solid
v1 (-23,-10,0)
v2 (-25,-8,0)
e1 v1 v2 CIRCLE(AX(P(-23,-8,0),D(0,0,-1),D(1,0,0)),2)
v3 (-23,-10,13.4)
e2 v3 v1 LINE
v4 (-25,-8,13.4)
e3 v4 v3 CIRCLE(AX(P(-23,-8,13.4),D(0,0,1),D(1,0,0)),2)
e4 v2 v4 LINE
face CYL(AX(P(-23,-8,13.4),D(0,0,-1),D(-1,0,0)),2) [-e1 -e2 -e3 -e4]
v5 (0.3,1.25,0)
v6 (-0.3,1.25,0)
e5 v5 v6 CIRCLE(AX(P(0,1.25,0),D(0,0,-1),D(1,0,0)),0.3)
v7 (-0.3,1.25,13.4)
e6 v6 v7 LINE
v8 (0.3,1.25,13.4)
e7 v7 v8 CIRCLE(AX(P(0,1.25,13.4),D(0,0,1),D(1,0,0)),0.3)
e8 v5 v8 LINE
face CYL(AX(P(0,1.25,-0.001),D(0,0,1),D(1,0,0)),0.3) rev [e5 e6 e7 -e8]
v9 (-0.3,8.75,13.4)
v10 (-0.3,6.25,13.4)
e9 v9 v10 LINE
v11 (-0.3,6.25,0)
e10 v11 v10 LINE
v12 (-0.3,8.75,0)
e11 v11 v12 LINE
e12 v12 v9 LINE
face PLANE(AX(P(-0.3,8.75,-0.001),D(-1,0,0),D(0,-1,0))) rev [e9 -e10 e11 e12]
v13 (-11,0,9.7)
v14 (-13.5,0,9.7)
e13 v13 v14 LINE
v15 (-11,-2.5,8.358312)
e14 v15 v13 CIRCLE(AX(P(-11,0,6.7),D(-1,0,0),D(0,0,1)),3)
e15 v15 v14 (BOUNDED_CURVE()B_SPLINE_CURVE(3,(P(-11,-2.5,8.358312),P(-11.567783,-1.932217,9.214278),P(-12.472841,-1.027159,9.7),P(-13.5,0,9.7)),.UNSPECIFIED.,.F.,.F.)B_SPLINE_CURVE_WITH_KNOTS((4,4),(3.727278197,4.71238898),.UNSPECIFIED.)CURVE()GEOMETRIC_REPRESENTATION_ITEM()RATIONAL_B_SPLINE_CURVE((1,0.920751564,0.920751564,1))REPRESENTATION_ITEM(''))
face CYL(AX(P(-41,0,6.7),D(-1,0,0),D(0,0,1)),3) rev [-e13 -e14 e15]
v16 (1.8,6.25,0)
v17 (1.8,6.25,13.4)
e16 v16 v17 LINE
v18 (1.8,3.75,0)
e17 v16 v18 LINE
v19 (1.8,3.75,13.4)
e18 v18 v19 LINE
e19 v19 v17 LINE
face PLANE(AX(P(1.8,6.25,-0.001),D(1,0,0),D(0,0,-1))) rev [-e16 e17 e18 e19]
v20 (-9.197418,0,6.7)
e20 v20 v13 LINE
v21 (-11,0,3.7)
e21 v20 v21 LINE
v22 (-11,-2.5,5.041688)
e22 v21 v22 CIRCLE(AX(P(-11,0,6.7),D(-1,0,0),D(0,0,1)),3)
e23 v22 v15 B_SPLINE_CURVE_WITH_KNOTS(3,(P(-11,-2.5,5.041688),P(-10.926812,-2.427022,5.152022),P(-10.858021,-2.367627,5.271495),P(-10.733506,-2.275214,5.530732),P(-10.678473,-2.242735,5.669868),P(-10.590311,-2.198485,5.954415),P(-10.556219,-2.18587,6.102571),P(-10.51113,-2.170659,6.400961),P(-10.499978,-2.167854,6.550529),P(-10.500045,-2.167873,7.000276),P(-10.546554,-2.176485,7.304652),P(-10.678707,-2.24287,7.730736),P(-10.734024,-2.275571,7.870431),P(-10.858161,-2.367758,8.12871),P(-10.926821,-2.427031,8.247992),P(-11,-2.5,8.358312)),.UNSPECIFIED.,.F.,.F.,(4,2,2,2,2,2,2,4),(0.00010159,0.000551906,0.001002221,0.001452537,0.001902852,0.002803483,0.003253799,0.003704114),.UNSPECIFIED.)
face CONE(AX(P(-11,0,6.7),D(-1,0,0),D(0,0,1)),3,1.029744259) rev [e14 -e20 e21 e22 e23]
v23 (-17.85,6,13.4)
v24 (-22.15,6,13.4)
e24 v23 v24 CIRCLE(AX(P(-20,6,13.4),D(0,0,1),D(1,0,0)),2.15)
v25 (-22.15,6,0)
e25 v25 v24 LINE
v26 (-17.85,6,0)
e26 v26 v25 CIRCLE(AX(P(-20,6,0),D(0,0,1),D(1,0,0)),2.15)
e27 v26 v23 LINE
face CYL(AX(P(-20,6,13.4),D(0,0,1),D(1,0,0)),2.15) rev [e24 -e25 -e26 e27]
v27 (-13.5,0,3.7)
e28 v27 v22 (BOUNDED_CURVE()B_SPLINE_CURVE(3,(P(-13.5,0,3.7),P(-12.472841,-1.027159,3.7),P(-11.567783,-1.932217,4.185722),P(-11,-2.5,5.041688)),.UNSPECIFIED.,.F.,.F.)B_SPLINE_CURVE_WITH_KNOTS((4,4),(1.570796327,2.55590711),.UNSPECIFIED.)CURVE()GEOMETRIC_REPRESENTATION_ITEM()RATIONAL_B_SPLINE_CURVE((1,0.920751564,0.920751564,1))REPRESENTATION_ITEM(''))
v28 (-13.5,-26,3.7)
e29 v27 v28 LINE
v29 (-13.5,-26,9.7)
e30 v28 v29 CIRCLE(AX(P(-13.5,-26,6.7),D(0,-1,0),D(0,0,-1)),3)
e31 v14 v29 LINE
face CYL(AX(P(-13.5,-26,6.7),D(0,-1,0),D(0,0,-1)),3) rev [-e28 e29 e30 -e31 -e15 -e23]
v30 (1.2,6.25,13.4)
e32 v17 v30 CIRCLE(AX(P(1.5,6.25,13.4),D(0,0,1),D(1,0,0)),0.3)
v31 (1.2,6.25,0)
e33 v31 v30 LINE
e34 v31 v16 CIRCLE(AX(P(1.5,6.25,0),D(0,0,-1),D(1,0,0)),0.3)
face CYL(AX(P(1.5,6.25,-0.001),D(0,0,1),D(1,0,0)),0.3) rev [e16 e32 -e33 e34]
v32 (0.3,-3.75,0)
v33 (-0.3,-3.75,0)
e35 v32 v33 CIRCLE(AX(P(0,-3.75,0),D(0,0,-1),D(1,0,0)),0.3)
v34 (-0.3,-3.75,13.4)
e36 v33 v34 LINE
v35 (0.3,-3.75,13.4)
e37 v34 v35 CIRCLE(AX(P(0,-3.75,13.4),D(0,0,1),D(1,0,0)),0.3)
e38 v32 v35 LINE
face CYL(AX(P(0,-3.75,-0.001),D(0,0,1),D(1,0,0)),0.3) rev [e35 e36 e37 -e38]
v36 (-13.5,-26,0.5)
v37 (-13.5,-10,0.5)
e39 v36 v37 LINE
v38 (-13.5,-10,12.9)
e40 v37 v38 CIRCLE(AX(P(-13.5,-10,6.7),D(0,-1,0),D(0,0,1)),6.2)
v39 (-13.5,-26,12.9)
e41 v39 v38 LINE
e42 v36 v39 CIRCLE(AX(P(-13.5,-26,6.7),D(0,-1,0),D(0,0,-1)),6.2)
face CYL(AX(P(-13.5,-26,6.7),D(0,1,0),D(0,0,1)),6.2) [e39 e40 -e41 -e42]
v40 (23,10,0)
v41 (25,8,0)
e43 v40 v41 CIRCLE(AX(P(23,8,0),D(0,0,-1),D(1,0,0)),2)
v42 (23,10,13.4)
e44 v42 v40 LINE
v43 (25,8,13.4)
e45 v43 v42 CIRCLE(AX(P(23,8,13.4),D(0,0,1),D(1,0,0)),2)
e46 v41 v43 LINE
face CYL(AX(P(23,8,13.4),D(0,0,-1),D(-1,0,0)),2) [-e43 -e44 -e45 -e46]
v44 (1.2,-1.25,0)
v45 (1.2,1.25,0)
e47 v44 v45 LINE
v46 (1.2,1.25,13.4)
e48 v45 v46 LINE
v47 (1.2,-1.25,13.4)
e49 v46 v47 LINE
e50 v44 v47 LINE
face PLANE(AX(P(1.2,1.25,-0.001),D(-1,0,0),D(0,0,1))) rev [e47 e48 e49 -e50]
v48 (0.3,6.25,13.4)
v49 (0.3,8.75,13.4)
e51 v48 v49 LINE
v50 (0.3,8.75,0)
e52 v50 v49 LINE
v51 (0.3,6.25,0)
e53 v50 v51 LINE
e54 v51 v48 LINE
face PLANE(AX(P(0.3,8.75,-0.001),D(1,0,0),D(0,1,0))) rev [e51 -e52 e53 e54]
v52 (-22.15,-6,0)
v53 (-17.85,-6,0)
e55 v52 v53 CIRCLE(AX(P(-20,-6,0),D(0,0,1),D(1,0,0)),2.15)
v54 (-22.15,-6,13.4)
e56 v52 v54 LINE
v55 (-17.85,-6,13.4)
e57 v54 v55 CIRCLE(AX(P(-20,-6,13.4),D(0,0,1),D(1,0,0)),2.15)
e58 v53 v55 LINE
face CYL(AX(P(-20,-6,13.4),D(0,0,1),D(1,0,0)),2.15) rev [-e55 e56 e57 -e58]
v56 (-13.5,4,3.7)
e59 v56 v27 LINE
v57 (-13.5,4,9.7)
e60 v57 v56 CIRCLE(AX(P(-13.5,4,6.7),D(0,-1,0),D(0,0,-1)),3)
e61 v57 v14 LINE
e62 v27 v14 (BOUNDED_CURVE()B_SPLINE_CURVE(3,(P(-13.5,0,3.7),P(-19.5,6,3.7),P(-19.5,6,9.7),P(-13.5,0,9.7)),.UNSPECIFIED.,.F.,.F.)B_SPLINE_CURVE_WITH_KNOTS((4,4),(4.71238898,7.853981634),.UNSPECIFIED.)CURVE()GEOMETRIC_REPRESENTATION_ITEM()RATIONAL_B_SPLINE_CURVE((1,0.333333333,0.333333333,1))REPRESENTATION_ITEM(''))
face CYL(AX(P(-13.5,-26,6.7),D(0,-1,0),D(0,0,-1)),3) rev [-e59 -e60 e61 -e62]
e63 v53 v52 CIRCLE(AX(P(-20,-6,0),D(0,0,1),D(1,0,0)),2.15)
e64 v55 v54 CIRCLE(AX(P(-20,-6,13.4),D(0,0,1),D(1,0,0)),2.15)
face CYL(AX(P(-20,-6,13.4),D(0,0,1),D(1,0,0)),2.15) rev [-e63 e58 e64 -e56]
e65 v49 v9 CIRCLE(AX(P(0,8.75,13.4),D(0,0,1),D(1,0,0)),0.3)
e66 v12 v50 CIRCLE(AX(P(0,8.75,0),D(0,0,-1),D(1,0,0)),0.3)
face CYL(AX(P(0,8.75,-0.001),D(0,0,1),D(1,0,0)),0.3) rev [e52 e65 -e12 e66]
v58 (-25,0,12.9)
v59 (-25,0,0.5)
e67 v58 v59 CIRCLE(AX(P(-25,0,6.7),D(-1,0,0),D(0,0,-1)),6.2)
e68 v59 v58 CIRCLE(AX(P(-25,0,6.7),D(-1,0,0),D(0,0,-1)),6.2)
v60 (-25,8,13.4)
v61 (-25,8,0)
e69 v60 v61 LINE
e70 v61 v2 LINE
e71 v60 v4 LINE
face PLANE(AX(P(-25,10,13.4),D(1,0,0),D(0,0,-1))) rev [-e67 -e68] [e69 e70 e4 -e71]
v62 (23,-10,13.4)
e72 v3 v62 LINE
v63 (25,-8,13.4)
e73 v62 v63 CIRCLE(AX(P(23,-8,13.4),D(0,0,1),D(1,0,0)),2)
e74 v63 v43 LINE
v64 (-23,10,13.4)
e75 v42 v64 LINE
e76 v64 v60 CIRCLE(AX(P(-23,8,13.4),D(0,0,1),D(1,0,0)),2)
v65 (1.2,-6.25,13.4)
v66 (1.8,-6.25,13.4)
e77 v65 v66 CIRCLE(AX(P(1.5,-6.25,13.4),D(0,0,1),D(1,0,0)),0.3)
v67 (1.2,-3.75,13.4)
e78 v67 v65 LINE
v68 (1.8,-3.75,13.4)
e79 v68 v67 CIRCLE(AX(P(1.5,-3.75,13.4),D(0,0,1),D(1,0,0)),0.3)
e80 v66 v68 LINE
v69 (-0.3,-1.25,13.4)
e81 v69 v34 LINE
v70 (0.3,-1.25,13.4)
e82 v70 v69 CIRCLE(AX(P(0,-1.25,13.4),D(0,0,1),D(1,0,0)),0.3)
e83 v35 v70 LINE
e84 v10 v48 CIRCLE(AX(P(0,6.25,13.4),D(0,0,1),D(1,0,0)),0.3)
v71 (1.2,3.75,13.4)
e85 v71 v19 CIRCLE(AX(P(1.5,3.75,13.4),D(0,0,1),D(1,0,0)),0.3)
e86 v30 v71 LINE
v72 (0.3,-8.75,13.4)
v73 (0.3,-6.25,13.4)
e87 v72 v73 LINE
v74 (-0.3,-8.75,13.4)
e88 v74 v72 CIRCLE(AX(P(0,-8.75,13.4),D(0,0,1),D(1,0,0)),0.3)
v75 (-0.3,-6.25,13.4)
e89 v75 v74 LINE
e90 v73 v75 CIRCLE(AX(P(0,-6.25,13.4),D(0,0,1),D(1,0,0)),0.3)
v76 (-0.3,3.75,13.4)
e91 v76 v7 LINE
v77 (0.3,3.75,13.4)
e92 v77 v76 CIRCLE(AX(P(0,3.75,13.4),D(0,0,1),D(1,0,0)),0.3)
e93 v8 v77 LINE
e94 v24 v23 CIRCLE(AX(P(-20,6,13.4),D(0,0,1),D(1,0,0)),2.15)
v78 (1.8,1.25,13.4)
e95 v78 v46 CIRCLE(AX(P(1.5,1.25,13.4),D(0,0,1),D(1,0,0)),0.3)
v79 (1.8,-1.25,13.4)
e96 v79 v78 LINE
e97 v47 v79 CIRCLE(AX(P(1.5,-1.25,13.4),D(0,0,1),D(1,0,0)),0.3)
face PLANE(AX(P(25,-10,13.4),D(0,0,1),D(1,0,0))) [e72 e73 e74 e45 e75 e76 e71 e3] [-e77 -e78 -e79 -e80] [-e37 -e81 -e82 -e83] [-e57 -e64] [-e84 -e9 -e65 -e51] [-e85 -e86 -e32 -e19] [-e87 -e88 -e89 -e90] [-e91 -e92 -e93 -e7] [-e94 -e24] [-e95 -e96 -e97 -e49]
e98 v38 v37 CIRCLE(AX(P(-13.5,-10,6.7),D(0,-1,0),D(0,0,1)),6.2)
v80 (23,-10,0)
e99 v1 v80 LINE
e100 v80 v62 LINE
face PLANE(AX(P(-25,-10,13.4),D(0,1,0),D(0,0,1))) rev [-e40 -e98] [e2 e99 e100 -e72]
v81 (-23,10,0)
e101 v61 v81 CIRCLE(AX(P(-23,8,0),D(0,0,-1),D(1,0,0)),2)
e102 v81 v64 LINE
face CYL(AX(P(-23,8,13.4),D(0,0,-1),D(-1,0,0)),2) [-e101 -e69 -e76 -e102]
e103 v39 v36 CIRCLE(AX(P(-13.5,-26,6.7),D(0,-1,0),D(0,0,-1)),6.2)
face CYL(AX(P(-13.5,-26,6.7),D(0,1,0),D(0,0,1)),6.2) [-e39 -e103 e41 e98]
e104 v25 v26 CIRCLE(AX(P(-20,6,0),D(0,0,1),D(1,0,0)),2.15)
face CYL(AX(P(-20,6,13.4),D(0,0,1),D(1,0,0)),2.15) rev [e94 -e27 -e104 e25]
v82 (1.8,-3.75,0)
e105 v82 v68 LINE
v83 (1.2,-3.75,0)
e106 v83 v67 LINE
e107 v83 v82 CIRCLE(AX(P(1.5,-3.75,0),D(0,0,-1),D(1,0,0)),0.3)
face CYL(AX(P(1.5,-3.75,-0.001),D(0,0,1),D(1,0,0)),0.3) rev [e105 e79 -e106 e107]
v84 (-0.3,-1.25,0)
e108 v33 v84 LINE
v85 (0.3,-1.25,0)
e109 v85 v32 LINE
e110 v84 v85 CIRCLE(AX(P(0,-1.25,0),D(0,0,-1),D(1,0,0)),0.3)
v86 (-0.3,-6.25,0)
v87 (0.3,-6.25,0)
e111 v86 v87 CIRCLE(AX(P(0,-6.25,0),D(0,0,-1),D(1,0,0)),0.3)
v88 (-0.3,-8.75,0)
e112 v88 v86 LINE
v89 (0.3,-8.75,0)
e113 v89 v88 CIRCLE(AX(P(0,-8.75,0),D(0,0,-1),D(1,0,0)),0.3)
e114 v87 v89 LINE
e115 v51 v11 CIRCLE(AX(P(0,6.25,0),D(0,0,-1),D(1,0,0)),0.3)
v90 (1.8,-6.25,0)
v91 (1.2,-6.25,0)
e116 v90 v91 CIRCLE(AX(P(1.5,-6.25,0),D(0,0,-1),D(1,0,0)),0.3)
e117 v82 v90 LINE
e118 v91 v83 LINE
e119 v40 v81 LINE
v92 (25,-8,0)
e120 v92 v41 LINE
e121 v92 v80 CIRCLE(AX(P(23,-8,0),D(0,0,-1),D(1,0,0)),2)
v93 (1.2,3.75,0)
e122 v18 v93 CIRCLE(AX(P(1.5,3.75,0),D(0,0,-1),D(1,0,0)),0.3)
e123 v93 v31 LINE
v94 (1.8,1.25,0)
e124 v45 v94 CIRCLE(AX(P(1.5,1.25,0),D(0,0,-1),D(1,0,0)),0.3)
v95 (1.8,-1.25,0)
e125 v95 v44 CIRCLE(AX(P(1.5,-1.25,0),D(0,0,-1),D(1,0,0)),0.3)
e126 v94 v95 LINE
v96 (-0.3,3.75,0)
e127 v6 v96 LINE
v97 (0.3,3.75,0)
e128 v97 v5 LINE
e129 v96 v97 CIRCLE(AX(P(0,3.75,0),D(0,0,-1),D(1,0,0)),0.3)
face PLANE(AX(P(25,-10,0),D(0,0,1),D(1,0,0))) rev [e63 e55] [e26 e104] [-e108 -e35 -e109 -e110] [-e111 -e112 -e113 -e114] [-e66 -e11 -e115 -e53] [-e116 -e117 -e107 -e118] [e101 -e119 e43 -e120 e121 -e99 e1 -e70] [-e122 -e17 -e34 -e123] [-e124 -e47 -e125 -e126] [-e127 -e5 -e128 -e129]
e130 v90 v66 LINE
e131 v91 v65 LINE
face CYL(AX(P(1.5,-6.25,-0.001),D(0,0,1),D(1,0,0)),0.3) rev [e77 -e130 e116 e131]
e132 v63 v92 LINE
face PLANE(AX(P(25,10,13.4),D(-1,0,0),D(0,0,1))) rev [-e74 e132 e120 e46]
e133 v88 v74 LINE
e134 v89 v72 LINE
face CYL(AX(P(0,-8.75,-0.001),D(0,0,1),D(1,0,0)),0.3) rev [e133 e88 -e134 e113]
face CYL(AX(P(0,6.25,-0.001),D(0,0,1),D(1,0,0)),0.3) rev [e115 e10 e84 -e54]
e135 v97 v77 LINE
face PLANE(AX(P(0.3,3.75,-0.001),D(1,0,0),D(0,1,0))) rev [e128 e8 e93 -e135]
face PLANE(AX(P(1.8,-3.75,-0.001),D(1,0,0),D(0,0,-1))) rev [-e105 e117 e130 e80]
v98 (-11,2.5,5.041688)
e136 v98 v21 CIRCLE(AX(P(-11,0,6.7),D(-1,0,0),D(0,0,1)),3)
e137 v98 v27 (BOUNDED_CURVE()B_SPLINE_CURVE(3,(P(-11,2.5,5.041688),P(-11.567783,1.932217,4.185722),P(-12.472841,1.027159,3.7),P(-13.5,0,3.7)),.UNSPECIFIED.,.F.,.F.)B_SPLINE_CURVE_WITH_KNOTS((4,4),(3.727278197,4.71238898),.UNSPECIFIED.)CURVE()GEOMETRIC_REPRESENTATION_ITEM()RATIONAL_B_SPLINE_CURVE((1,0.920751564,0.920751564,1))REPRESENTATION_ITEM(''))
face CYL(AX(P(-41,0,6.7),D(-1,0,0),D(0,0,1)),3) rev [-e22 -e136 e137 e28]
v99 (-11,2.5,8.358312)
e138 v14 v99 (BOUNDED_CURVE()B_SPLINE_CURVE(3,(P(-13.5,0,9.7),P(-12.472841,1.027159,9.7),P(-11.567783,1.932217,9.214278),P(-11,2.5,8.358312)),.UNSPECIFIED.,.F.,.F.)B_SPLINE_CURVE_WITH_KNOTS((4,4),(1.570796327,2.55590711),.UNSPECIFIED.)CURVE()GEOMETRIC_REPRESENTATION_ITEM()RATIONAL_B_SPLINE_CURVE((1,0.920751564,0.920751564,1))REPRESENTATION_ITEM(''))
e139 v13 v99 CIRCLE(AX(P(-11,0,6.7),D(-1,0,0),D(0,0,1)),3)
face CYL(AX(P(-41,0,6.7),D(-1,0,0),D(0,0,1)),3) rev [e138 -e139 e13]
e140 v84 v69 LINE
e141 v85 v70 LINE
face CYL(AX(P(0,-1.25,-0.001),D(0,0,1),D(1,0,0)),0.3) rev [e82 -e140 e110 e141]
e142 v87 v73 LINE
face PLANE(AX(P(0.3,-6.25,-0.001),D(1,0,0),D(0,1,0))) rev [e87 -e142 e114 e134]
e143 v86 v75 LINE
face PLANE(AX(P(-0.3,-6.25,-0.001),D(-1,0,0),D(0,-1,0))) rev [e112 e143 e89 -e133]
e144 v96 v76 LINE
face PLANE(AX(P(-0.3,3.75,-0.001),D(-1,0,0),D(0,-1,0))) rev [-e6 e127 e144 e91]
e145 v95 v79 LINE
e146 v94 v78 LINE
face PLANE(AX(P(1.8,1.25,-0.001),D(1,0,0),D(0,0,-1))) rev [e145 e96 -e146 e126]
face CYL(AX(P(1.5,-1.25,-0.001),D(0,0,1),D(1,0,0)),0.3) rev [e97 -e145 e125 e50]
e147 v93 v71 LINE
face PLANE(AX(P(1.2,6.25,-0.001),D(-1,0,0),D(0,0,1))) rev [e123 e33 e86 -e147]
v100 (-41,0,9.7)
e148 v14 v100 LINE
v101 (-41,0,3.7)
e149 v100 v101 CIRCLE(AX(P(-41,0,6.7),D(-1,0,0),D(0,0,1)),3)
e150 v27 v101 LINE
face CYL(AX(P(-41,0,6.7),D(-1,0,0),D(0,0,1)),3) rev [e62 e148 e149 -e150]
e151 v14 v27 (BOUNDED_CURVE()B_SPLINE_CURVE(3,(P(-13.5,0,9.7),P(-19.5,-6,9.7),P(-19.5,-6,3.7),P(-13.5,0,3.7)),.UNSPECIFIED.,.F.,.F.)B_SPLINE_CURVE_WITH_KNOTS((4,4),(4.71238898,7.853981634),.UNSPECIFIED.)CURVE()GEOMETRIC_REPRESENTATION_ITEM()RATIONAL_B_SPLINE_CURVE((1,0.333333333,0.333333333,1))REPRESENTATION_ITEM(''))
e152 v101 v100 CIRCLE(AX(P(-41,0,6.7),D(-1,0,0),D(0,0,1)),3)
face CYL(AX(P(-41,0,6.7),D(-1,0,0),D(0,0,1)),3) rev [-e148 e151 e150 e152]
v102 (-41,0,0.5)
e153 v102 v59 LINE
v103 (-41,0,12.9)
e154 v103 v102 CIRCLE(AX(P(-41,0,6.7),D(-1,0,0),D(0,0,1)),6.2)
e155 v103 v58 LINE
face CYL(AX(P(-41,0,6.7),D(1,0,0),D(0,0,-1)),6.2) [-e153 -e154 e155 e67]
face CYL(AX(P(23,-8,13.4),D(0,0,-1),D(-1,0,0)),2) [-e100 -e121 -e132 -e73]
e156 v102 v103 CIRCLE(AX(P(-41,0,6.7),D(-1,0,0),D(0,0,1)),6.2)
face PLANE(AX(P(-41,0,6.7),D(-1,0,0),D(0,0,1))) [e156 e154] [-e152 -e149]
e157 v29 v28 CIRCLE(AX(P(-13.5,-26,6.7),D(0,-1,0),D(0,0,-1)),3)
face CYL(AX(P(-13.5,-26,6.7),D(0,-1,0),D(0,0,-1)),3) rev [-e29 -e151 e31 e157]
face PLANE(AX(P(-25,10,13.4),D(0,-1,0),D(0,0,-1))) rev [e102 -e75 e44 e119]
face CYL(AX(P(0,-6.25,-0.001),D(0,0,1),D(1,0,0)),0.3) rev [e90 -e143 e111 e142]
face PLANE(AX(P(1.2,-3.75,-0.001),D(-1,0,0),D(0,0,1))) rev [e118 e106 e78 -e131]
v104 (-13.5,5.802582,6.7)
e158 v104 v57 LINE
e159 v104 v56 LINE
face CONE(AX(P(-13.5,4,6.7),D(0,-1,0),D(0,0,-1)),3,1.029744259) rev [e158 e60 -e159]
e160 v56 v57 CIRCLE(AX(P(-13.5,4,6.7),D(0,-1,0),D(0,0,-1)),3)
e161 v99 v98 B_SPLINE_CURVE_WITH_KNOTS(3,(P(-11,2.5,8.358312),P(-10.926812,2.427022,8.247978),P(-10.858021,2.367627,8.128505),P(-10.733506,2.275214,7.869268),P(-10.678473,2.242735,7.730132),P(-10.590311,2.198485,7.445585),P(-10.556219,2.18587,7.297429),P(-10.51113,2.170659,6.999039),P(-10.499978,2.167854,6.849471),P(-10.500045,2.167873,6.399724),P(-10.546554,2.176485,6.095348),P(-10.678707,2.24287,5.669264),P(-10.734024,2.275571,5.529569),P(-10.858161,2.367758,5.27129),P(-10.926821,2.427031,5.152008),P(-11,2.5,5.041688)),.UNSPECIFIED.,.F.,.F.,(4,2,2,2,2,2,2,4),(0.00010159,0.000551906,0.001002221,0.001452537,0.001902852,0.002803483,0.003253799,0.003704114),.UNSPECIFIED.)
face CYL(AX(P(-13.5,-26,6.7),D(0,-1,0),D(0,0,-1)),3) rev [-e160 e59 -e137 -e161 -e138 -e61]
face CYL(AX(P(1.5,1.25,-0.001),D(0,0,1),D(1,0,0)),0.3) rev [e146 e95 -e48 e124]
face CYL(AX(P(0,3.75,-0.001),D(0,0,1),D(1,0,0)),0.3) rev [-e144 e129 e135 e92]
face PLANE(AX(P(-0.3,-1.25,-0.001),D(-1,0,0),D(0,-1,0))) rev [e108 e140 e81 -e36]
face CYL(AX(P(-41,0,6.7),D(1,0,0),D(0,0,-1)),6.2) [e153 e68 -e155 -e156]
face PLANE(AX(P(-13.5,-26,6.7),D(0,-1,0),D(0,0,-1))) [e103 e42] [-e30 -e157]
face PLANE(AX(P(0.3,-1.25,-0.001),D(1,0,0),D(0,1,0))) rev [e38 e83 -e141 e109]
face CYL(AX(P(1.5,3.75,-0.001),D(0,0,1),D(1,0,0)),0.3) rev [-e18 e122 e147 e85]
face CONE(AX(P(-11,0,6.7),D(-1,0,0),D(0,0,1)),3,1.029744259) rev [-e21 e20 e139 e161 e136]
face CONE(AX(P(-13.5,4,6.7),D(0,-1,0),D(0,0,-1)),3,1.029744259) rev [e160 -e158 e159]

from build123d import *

# Parameters (mm, degrees)
SKETCH_1_W                  = 50
SKETCH_1_H                  = 20
EXTRUDE_1_DEPTH             = 13.4
SKETCH_2_R                  = 6.2
EXTRUDE_2_DEPTH             = 16
SKETCH_3_R                  = 6.2
EXTRUDE_3_DEPTH             = 16
HOLE_WIZARD_6_0_6_1_D       = 6
HOLE_WIZARD_6_0_6_1_DEPTH   = 30
HOLE_WIZARD_6_0_6_1_TIP     = 1.802581857
HOLE_WIZARD_6_0_6_2_D       = 6
HOLE_WIZARD_6_0_6_2_DEPTH   = 30
HOLE_WIZARD_6_0_6_2_TIP     = 1.802581857
HOLE_WIZARD_4_3_4_3_1_D     = 4.3
HOLE_WIZARD_4_3_4_3_1_DEPTH = 30
HOLE_WIZARD_4_3_4_3_1_TIP   = 1.291850331
FILLET_1_R                  = 2
CUT_EXTRUDE_1_REACH         = 52.364
PATTERN_LINEAR_1_COUNT      = 4
PATTERN_LINEAR_1_PITCH      = 5
CUT_EXTRUDE_2_REACH         = 52.364
PATTERN_LINEAR_2_COUNT      = 3
PATTERN_LINEAR_2_PITCH      = 5


with BuildPart() as part:
    # 草图1 → 凸台-拉伸1 (new body)
    with BuildSketch(Plane.XY):
        Rectangle(SKETCH_1_W, SKETCH_1_H)
    extrude(amount=EXTRUDE_1_DEPTH)

    # 草图2 → 凸台-拉伸2 (add)
    with BuildSketch(Plane.XZ.offset(10)):
        with Locations(Location((-13.5, 6.7, 0), (0, 0, 90))):
            Circle(SKETCH_2_R)
    extrude(amount=EXTRUDE_2_DEPTH)

    # 草图3 → 凸台-拉伸3 (add)
    with BuildSketch(Plane.ZY.offset(25)):
        with Locations(Location((6.7, 0, 0), (0, 0, 180))):
            Circle(SKETCH_3_R)
    extrude(amount=EXTRUDE_3_DEPTH)

    # Ø6.0 (6) 直径孔1
    with Locations(Plane.ZY.offset(41)):
        with Locations((6.7, 0)):
            Hole(HOLE_WIZARD_6_0_6_1_D / 2, depth=HOLE_WIZARD_6_0_6_1_DEPTH)
            with Locations((0, 0, -(HOLE_WIZARD_6_0_6_1_DEPTH + HOLE_WIZARD_6_0_6_1_TIP / 2))):  # 118° drill point
                Cone(0, HOLE_WIZARD_6_0_6_1_D / 2, HOLE_WIZARD_6_0_6_1_TIP, mode=Mode.SUBTRACT)

    # Ø6.0 (6) 直径孔2
    with Locations(Plane.XZ.offset(26)):
        with Locations((-13.5, 6.7)):
            Hole(HOLE_WIZARD_6_0_6_2_D / 2, depth=HOLE_WIZARD_6_0_6_2_DEPTH)
            with Locations((0, 0, -(HOLE_WIZARD_6_0_6_2_DEPTH + HOLE_WIZARD_6_0_6_2_TIP / 2))):  # 118° drill point
                Cone(0, HOLE_WIZARD_6_0_6_2_D / 2, HOLE_WIZARD_6_0_6_2_TIP, mode=Mode.SUBTRACT)

    # Ø4.3 (4.3) 直径孔1
    with Locations(Plane.XY.offset(13.4)):
        with Locations((-20, 6), (-20, -6)):
            Hole(HOLE_WIZARD_4_3_4_3_1_D / 2, depth=HOLE_WIZARD_4_3_4_3_1_DEPTH)
            with Locations((0, 0, -(HOLE_WIZARD_4_3_4_3_1_DEPTH + HOLE_WIZARD_4_3_4_3_1_TIP / 2))):  # 118° drill point
                Cone(0, HOLE_WIZARD_4_3_4_3_1_D / 2, HOLE_WIZARD_4_3_4_3_1_TIP, mode=Mode.SUBTRACT)

    # 圆角1
    fillet_1_edges = [part.edges().sort_by_distance(p)[0] for p in [
        (25, -10, 6.7),
        (-25, -10, 6.7),
        (-25, 10, 6.7),
        (25, 10, 6.7),
    ]]
    fillet(fillet_1_edges, radius=FILLET_1_R)

    # 草图11 → 切除-拉伸1 (cut, up to next)
    with BuildSketch(Plane.XY.offset(13.4), mode=Mode.PRIVATE) as cut_extrude_1_sk1:
        with BuildLine():
            Line((0.3, 8.75), (0.3, 6.25))
            ThreePointArc((0.3, 6.25), (0, 5.95), (-0.3, 6.25))
            Line((-0.3, 6.25), (-0.3, 8.75))
            ThreePointArc((-0.3, 8.75), (0, 9.05), (0.3, 8.75))
        make_face()
    cut_extrude_1_tool1 = extrude(cut_extrude_1_sk1.sketch, amount=-CUT_EXTRUDE_1_REACH, mode=Mode.PRIVATE) & part.part
    cut_extrude_1 = cut_extrude_1_tool1.solids().sort_by_distance((0, 7.5, 13.4))[0]
    add(cut_extrude_1, mode=Mode.SUBTRACT)

    # 阵列(线性)1: 切除-拉伸1 ×4
    with Locations(*[(0, -i * PATTERN_LINEAR_1_PITCH, 0) for i in range(1, PATTERN_LINEAR_1_COUNT)]):
        add(cut_extrude_1, mode=Mode.SUBTRACT)

    # 草图12 → 切除-拉伸2 (cut, up to next)
    with BuildSketch(Plane.XY.offset(13.4), mode=Mode.PRIVATE) as cut_extrude_2_sk1:
        with BuildLine():
            Line((1.8, 6.25), (1.8, 3.75))
            ThreePointArc((1.8, 3.75), (1.5, 3.45), (1.2, 3.75))
            Line((1.2, 3.75), (1.2, 6.25))
            ThreePointArc((1.2, 6.25), (1.5, 6.55), (1.8, 6.25))
        make_face()
    cut_extrude_2_tool1 = extrude(cut_extrude_2_sk1.sketch, amount=-CUT_EXTRUDE_2_REACH, mode=Mode.PRIVATE) & part.part
    cut_extrude_2 = cut_extrude_2_tool1.solids().sort_by_distance((1.5, 5, 13.4))[0]
    add(cut_extrude_2, mode=Mode.SUBTRACT)

    # 阵列(线性)2: 切除-拉伸2 ×3
    with Locations(*[(0, -i * PATTERN_LINEAR_2_PITCH, 0) for i in range(1, PATTERN_LINEAR_2_COUNT)]):
        add(cut_extrude_2, mode=Mode.SUBTRACT)


solid = part.part
